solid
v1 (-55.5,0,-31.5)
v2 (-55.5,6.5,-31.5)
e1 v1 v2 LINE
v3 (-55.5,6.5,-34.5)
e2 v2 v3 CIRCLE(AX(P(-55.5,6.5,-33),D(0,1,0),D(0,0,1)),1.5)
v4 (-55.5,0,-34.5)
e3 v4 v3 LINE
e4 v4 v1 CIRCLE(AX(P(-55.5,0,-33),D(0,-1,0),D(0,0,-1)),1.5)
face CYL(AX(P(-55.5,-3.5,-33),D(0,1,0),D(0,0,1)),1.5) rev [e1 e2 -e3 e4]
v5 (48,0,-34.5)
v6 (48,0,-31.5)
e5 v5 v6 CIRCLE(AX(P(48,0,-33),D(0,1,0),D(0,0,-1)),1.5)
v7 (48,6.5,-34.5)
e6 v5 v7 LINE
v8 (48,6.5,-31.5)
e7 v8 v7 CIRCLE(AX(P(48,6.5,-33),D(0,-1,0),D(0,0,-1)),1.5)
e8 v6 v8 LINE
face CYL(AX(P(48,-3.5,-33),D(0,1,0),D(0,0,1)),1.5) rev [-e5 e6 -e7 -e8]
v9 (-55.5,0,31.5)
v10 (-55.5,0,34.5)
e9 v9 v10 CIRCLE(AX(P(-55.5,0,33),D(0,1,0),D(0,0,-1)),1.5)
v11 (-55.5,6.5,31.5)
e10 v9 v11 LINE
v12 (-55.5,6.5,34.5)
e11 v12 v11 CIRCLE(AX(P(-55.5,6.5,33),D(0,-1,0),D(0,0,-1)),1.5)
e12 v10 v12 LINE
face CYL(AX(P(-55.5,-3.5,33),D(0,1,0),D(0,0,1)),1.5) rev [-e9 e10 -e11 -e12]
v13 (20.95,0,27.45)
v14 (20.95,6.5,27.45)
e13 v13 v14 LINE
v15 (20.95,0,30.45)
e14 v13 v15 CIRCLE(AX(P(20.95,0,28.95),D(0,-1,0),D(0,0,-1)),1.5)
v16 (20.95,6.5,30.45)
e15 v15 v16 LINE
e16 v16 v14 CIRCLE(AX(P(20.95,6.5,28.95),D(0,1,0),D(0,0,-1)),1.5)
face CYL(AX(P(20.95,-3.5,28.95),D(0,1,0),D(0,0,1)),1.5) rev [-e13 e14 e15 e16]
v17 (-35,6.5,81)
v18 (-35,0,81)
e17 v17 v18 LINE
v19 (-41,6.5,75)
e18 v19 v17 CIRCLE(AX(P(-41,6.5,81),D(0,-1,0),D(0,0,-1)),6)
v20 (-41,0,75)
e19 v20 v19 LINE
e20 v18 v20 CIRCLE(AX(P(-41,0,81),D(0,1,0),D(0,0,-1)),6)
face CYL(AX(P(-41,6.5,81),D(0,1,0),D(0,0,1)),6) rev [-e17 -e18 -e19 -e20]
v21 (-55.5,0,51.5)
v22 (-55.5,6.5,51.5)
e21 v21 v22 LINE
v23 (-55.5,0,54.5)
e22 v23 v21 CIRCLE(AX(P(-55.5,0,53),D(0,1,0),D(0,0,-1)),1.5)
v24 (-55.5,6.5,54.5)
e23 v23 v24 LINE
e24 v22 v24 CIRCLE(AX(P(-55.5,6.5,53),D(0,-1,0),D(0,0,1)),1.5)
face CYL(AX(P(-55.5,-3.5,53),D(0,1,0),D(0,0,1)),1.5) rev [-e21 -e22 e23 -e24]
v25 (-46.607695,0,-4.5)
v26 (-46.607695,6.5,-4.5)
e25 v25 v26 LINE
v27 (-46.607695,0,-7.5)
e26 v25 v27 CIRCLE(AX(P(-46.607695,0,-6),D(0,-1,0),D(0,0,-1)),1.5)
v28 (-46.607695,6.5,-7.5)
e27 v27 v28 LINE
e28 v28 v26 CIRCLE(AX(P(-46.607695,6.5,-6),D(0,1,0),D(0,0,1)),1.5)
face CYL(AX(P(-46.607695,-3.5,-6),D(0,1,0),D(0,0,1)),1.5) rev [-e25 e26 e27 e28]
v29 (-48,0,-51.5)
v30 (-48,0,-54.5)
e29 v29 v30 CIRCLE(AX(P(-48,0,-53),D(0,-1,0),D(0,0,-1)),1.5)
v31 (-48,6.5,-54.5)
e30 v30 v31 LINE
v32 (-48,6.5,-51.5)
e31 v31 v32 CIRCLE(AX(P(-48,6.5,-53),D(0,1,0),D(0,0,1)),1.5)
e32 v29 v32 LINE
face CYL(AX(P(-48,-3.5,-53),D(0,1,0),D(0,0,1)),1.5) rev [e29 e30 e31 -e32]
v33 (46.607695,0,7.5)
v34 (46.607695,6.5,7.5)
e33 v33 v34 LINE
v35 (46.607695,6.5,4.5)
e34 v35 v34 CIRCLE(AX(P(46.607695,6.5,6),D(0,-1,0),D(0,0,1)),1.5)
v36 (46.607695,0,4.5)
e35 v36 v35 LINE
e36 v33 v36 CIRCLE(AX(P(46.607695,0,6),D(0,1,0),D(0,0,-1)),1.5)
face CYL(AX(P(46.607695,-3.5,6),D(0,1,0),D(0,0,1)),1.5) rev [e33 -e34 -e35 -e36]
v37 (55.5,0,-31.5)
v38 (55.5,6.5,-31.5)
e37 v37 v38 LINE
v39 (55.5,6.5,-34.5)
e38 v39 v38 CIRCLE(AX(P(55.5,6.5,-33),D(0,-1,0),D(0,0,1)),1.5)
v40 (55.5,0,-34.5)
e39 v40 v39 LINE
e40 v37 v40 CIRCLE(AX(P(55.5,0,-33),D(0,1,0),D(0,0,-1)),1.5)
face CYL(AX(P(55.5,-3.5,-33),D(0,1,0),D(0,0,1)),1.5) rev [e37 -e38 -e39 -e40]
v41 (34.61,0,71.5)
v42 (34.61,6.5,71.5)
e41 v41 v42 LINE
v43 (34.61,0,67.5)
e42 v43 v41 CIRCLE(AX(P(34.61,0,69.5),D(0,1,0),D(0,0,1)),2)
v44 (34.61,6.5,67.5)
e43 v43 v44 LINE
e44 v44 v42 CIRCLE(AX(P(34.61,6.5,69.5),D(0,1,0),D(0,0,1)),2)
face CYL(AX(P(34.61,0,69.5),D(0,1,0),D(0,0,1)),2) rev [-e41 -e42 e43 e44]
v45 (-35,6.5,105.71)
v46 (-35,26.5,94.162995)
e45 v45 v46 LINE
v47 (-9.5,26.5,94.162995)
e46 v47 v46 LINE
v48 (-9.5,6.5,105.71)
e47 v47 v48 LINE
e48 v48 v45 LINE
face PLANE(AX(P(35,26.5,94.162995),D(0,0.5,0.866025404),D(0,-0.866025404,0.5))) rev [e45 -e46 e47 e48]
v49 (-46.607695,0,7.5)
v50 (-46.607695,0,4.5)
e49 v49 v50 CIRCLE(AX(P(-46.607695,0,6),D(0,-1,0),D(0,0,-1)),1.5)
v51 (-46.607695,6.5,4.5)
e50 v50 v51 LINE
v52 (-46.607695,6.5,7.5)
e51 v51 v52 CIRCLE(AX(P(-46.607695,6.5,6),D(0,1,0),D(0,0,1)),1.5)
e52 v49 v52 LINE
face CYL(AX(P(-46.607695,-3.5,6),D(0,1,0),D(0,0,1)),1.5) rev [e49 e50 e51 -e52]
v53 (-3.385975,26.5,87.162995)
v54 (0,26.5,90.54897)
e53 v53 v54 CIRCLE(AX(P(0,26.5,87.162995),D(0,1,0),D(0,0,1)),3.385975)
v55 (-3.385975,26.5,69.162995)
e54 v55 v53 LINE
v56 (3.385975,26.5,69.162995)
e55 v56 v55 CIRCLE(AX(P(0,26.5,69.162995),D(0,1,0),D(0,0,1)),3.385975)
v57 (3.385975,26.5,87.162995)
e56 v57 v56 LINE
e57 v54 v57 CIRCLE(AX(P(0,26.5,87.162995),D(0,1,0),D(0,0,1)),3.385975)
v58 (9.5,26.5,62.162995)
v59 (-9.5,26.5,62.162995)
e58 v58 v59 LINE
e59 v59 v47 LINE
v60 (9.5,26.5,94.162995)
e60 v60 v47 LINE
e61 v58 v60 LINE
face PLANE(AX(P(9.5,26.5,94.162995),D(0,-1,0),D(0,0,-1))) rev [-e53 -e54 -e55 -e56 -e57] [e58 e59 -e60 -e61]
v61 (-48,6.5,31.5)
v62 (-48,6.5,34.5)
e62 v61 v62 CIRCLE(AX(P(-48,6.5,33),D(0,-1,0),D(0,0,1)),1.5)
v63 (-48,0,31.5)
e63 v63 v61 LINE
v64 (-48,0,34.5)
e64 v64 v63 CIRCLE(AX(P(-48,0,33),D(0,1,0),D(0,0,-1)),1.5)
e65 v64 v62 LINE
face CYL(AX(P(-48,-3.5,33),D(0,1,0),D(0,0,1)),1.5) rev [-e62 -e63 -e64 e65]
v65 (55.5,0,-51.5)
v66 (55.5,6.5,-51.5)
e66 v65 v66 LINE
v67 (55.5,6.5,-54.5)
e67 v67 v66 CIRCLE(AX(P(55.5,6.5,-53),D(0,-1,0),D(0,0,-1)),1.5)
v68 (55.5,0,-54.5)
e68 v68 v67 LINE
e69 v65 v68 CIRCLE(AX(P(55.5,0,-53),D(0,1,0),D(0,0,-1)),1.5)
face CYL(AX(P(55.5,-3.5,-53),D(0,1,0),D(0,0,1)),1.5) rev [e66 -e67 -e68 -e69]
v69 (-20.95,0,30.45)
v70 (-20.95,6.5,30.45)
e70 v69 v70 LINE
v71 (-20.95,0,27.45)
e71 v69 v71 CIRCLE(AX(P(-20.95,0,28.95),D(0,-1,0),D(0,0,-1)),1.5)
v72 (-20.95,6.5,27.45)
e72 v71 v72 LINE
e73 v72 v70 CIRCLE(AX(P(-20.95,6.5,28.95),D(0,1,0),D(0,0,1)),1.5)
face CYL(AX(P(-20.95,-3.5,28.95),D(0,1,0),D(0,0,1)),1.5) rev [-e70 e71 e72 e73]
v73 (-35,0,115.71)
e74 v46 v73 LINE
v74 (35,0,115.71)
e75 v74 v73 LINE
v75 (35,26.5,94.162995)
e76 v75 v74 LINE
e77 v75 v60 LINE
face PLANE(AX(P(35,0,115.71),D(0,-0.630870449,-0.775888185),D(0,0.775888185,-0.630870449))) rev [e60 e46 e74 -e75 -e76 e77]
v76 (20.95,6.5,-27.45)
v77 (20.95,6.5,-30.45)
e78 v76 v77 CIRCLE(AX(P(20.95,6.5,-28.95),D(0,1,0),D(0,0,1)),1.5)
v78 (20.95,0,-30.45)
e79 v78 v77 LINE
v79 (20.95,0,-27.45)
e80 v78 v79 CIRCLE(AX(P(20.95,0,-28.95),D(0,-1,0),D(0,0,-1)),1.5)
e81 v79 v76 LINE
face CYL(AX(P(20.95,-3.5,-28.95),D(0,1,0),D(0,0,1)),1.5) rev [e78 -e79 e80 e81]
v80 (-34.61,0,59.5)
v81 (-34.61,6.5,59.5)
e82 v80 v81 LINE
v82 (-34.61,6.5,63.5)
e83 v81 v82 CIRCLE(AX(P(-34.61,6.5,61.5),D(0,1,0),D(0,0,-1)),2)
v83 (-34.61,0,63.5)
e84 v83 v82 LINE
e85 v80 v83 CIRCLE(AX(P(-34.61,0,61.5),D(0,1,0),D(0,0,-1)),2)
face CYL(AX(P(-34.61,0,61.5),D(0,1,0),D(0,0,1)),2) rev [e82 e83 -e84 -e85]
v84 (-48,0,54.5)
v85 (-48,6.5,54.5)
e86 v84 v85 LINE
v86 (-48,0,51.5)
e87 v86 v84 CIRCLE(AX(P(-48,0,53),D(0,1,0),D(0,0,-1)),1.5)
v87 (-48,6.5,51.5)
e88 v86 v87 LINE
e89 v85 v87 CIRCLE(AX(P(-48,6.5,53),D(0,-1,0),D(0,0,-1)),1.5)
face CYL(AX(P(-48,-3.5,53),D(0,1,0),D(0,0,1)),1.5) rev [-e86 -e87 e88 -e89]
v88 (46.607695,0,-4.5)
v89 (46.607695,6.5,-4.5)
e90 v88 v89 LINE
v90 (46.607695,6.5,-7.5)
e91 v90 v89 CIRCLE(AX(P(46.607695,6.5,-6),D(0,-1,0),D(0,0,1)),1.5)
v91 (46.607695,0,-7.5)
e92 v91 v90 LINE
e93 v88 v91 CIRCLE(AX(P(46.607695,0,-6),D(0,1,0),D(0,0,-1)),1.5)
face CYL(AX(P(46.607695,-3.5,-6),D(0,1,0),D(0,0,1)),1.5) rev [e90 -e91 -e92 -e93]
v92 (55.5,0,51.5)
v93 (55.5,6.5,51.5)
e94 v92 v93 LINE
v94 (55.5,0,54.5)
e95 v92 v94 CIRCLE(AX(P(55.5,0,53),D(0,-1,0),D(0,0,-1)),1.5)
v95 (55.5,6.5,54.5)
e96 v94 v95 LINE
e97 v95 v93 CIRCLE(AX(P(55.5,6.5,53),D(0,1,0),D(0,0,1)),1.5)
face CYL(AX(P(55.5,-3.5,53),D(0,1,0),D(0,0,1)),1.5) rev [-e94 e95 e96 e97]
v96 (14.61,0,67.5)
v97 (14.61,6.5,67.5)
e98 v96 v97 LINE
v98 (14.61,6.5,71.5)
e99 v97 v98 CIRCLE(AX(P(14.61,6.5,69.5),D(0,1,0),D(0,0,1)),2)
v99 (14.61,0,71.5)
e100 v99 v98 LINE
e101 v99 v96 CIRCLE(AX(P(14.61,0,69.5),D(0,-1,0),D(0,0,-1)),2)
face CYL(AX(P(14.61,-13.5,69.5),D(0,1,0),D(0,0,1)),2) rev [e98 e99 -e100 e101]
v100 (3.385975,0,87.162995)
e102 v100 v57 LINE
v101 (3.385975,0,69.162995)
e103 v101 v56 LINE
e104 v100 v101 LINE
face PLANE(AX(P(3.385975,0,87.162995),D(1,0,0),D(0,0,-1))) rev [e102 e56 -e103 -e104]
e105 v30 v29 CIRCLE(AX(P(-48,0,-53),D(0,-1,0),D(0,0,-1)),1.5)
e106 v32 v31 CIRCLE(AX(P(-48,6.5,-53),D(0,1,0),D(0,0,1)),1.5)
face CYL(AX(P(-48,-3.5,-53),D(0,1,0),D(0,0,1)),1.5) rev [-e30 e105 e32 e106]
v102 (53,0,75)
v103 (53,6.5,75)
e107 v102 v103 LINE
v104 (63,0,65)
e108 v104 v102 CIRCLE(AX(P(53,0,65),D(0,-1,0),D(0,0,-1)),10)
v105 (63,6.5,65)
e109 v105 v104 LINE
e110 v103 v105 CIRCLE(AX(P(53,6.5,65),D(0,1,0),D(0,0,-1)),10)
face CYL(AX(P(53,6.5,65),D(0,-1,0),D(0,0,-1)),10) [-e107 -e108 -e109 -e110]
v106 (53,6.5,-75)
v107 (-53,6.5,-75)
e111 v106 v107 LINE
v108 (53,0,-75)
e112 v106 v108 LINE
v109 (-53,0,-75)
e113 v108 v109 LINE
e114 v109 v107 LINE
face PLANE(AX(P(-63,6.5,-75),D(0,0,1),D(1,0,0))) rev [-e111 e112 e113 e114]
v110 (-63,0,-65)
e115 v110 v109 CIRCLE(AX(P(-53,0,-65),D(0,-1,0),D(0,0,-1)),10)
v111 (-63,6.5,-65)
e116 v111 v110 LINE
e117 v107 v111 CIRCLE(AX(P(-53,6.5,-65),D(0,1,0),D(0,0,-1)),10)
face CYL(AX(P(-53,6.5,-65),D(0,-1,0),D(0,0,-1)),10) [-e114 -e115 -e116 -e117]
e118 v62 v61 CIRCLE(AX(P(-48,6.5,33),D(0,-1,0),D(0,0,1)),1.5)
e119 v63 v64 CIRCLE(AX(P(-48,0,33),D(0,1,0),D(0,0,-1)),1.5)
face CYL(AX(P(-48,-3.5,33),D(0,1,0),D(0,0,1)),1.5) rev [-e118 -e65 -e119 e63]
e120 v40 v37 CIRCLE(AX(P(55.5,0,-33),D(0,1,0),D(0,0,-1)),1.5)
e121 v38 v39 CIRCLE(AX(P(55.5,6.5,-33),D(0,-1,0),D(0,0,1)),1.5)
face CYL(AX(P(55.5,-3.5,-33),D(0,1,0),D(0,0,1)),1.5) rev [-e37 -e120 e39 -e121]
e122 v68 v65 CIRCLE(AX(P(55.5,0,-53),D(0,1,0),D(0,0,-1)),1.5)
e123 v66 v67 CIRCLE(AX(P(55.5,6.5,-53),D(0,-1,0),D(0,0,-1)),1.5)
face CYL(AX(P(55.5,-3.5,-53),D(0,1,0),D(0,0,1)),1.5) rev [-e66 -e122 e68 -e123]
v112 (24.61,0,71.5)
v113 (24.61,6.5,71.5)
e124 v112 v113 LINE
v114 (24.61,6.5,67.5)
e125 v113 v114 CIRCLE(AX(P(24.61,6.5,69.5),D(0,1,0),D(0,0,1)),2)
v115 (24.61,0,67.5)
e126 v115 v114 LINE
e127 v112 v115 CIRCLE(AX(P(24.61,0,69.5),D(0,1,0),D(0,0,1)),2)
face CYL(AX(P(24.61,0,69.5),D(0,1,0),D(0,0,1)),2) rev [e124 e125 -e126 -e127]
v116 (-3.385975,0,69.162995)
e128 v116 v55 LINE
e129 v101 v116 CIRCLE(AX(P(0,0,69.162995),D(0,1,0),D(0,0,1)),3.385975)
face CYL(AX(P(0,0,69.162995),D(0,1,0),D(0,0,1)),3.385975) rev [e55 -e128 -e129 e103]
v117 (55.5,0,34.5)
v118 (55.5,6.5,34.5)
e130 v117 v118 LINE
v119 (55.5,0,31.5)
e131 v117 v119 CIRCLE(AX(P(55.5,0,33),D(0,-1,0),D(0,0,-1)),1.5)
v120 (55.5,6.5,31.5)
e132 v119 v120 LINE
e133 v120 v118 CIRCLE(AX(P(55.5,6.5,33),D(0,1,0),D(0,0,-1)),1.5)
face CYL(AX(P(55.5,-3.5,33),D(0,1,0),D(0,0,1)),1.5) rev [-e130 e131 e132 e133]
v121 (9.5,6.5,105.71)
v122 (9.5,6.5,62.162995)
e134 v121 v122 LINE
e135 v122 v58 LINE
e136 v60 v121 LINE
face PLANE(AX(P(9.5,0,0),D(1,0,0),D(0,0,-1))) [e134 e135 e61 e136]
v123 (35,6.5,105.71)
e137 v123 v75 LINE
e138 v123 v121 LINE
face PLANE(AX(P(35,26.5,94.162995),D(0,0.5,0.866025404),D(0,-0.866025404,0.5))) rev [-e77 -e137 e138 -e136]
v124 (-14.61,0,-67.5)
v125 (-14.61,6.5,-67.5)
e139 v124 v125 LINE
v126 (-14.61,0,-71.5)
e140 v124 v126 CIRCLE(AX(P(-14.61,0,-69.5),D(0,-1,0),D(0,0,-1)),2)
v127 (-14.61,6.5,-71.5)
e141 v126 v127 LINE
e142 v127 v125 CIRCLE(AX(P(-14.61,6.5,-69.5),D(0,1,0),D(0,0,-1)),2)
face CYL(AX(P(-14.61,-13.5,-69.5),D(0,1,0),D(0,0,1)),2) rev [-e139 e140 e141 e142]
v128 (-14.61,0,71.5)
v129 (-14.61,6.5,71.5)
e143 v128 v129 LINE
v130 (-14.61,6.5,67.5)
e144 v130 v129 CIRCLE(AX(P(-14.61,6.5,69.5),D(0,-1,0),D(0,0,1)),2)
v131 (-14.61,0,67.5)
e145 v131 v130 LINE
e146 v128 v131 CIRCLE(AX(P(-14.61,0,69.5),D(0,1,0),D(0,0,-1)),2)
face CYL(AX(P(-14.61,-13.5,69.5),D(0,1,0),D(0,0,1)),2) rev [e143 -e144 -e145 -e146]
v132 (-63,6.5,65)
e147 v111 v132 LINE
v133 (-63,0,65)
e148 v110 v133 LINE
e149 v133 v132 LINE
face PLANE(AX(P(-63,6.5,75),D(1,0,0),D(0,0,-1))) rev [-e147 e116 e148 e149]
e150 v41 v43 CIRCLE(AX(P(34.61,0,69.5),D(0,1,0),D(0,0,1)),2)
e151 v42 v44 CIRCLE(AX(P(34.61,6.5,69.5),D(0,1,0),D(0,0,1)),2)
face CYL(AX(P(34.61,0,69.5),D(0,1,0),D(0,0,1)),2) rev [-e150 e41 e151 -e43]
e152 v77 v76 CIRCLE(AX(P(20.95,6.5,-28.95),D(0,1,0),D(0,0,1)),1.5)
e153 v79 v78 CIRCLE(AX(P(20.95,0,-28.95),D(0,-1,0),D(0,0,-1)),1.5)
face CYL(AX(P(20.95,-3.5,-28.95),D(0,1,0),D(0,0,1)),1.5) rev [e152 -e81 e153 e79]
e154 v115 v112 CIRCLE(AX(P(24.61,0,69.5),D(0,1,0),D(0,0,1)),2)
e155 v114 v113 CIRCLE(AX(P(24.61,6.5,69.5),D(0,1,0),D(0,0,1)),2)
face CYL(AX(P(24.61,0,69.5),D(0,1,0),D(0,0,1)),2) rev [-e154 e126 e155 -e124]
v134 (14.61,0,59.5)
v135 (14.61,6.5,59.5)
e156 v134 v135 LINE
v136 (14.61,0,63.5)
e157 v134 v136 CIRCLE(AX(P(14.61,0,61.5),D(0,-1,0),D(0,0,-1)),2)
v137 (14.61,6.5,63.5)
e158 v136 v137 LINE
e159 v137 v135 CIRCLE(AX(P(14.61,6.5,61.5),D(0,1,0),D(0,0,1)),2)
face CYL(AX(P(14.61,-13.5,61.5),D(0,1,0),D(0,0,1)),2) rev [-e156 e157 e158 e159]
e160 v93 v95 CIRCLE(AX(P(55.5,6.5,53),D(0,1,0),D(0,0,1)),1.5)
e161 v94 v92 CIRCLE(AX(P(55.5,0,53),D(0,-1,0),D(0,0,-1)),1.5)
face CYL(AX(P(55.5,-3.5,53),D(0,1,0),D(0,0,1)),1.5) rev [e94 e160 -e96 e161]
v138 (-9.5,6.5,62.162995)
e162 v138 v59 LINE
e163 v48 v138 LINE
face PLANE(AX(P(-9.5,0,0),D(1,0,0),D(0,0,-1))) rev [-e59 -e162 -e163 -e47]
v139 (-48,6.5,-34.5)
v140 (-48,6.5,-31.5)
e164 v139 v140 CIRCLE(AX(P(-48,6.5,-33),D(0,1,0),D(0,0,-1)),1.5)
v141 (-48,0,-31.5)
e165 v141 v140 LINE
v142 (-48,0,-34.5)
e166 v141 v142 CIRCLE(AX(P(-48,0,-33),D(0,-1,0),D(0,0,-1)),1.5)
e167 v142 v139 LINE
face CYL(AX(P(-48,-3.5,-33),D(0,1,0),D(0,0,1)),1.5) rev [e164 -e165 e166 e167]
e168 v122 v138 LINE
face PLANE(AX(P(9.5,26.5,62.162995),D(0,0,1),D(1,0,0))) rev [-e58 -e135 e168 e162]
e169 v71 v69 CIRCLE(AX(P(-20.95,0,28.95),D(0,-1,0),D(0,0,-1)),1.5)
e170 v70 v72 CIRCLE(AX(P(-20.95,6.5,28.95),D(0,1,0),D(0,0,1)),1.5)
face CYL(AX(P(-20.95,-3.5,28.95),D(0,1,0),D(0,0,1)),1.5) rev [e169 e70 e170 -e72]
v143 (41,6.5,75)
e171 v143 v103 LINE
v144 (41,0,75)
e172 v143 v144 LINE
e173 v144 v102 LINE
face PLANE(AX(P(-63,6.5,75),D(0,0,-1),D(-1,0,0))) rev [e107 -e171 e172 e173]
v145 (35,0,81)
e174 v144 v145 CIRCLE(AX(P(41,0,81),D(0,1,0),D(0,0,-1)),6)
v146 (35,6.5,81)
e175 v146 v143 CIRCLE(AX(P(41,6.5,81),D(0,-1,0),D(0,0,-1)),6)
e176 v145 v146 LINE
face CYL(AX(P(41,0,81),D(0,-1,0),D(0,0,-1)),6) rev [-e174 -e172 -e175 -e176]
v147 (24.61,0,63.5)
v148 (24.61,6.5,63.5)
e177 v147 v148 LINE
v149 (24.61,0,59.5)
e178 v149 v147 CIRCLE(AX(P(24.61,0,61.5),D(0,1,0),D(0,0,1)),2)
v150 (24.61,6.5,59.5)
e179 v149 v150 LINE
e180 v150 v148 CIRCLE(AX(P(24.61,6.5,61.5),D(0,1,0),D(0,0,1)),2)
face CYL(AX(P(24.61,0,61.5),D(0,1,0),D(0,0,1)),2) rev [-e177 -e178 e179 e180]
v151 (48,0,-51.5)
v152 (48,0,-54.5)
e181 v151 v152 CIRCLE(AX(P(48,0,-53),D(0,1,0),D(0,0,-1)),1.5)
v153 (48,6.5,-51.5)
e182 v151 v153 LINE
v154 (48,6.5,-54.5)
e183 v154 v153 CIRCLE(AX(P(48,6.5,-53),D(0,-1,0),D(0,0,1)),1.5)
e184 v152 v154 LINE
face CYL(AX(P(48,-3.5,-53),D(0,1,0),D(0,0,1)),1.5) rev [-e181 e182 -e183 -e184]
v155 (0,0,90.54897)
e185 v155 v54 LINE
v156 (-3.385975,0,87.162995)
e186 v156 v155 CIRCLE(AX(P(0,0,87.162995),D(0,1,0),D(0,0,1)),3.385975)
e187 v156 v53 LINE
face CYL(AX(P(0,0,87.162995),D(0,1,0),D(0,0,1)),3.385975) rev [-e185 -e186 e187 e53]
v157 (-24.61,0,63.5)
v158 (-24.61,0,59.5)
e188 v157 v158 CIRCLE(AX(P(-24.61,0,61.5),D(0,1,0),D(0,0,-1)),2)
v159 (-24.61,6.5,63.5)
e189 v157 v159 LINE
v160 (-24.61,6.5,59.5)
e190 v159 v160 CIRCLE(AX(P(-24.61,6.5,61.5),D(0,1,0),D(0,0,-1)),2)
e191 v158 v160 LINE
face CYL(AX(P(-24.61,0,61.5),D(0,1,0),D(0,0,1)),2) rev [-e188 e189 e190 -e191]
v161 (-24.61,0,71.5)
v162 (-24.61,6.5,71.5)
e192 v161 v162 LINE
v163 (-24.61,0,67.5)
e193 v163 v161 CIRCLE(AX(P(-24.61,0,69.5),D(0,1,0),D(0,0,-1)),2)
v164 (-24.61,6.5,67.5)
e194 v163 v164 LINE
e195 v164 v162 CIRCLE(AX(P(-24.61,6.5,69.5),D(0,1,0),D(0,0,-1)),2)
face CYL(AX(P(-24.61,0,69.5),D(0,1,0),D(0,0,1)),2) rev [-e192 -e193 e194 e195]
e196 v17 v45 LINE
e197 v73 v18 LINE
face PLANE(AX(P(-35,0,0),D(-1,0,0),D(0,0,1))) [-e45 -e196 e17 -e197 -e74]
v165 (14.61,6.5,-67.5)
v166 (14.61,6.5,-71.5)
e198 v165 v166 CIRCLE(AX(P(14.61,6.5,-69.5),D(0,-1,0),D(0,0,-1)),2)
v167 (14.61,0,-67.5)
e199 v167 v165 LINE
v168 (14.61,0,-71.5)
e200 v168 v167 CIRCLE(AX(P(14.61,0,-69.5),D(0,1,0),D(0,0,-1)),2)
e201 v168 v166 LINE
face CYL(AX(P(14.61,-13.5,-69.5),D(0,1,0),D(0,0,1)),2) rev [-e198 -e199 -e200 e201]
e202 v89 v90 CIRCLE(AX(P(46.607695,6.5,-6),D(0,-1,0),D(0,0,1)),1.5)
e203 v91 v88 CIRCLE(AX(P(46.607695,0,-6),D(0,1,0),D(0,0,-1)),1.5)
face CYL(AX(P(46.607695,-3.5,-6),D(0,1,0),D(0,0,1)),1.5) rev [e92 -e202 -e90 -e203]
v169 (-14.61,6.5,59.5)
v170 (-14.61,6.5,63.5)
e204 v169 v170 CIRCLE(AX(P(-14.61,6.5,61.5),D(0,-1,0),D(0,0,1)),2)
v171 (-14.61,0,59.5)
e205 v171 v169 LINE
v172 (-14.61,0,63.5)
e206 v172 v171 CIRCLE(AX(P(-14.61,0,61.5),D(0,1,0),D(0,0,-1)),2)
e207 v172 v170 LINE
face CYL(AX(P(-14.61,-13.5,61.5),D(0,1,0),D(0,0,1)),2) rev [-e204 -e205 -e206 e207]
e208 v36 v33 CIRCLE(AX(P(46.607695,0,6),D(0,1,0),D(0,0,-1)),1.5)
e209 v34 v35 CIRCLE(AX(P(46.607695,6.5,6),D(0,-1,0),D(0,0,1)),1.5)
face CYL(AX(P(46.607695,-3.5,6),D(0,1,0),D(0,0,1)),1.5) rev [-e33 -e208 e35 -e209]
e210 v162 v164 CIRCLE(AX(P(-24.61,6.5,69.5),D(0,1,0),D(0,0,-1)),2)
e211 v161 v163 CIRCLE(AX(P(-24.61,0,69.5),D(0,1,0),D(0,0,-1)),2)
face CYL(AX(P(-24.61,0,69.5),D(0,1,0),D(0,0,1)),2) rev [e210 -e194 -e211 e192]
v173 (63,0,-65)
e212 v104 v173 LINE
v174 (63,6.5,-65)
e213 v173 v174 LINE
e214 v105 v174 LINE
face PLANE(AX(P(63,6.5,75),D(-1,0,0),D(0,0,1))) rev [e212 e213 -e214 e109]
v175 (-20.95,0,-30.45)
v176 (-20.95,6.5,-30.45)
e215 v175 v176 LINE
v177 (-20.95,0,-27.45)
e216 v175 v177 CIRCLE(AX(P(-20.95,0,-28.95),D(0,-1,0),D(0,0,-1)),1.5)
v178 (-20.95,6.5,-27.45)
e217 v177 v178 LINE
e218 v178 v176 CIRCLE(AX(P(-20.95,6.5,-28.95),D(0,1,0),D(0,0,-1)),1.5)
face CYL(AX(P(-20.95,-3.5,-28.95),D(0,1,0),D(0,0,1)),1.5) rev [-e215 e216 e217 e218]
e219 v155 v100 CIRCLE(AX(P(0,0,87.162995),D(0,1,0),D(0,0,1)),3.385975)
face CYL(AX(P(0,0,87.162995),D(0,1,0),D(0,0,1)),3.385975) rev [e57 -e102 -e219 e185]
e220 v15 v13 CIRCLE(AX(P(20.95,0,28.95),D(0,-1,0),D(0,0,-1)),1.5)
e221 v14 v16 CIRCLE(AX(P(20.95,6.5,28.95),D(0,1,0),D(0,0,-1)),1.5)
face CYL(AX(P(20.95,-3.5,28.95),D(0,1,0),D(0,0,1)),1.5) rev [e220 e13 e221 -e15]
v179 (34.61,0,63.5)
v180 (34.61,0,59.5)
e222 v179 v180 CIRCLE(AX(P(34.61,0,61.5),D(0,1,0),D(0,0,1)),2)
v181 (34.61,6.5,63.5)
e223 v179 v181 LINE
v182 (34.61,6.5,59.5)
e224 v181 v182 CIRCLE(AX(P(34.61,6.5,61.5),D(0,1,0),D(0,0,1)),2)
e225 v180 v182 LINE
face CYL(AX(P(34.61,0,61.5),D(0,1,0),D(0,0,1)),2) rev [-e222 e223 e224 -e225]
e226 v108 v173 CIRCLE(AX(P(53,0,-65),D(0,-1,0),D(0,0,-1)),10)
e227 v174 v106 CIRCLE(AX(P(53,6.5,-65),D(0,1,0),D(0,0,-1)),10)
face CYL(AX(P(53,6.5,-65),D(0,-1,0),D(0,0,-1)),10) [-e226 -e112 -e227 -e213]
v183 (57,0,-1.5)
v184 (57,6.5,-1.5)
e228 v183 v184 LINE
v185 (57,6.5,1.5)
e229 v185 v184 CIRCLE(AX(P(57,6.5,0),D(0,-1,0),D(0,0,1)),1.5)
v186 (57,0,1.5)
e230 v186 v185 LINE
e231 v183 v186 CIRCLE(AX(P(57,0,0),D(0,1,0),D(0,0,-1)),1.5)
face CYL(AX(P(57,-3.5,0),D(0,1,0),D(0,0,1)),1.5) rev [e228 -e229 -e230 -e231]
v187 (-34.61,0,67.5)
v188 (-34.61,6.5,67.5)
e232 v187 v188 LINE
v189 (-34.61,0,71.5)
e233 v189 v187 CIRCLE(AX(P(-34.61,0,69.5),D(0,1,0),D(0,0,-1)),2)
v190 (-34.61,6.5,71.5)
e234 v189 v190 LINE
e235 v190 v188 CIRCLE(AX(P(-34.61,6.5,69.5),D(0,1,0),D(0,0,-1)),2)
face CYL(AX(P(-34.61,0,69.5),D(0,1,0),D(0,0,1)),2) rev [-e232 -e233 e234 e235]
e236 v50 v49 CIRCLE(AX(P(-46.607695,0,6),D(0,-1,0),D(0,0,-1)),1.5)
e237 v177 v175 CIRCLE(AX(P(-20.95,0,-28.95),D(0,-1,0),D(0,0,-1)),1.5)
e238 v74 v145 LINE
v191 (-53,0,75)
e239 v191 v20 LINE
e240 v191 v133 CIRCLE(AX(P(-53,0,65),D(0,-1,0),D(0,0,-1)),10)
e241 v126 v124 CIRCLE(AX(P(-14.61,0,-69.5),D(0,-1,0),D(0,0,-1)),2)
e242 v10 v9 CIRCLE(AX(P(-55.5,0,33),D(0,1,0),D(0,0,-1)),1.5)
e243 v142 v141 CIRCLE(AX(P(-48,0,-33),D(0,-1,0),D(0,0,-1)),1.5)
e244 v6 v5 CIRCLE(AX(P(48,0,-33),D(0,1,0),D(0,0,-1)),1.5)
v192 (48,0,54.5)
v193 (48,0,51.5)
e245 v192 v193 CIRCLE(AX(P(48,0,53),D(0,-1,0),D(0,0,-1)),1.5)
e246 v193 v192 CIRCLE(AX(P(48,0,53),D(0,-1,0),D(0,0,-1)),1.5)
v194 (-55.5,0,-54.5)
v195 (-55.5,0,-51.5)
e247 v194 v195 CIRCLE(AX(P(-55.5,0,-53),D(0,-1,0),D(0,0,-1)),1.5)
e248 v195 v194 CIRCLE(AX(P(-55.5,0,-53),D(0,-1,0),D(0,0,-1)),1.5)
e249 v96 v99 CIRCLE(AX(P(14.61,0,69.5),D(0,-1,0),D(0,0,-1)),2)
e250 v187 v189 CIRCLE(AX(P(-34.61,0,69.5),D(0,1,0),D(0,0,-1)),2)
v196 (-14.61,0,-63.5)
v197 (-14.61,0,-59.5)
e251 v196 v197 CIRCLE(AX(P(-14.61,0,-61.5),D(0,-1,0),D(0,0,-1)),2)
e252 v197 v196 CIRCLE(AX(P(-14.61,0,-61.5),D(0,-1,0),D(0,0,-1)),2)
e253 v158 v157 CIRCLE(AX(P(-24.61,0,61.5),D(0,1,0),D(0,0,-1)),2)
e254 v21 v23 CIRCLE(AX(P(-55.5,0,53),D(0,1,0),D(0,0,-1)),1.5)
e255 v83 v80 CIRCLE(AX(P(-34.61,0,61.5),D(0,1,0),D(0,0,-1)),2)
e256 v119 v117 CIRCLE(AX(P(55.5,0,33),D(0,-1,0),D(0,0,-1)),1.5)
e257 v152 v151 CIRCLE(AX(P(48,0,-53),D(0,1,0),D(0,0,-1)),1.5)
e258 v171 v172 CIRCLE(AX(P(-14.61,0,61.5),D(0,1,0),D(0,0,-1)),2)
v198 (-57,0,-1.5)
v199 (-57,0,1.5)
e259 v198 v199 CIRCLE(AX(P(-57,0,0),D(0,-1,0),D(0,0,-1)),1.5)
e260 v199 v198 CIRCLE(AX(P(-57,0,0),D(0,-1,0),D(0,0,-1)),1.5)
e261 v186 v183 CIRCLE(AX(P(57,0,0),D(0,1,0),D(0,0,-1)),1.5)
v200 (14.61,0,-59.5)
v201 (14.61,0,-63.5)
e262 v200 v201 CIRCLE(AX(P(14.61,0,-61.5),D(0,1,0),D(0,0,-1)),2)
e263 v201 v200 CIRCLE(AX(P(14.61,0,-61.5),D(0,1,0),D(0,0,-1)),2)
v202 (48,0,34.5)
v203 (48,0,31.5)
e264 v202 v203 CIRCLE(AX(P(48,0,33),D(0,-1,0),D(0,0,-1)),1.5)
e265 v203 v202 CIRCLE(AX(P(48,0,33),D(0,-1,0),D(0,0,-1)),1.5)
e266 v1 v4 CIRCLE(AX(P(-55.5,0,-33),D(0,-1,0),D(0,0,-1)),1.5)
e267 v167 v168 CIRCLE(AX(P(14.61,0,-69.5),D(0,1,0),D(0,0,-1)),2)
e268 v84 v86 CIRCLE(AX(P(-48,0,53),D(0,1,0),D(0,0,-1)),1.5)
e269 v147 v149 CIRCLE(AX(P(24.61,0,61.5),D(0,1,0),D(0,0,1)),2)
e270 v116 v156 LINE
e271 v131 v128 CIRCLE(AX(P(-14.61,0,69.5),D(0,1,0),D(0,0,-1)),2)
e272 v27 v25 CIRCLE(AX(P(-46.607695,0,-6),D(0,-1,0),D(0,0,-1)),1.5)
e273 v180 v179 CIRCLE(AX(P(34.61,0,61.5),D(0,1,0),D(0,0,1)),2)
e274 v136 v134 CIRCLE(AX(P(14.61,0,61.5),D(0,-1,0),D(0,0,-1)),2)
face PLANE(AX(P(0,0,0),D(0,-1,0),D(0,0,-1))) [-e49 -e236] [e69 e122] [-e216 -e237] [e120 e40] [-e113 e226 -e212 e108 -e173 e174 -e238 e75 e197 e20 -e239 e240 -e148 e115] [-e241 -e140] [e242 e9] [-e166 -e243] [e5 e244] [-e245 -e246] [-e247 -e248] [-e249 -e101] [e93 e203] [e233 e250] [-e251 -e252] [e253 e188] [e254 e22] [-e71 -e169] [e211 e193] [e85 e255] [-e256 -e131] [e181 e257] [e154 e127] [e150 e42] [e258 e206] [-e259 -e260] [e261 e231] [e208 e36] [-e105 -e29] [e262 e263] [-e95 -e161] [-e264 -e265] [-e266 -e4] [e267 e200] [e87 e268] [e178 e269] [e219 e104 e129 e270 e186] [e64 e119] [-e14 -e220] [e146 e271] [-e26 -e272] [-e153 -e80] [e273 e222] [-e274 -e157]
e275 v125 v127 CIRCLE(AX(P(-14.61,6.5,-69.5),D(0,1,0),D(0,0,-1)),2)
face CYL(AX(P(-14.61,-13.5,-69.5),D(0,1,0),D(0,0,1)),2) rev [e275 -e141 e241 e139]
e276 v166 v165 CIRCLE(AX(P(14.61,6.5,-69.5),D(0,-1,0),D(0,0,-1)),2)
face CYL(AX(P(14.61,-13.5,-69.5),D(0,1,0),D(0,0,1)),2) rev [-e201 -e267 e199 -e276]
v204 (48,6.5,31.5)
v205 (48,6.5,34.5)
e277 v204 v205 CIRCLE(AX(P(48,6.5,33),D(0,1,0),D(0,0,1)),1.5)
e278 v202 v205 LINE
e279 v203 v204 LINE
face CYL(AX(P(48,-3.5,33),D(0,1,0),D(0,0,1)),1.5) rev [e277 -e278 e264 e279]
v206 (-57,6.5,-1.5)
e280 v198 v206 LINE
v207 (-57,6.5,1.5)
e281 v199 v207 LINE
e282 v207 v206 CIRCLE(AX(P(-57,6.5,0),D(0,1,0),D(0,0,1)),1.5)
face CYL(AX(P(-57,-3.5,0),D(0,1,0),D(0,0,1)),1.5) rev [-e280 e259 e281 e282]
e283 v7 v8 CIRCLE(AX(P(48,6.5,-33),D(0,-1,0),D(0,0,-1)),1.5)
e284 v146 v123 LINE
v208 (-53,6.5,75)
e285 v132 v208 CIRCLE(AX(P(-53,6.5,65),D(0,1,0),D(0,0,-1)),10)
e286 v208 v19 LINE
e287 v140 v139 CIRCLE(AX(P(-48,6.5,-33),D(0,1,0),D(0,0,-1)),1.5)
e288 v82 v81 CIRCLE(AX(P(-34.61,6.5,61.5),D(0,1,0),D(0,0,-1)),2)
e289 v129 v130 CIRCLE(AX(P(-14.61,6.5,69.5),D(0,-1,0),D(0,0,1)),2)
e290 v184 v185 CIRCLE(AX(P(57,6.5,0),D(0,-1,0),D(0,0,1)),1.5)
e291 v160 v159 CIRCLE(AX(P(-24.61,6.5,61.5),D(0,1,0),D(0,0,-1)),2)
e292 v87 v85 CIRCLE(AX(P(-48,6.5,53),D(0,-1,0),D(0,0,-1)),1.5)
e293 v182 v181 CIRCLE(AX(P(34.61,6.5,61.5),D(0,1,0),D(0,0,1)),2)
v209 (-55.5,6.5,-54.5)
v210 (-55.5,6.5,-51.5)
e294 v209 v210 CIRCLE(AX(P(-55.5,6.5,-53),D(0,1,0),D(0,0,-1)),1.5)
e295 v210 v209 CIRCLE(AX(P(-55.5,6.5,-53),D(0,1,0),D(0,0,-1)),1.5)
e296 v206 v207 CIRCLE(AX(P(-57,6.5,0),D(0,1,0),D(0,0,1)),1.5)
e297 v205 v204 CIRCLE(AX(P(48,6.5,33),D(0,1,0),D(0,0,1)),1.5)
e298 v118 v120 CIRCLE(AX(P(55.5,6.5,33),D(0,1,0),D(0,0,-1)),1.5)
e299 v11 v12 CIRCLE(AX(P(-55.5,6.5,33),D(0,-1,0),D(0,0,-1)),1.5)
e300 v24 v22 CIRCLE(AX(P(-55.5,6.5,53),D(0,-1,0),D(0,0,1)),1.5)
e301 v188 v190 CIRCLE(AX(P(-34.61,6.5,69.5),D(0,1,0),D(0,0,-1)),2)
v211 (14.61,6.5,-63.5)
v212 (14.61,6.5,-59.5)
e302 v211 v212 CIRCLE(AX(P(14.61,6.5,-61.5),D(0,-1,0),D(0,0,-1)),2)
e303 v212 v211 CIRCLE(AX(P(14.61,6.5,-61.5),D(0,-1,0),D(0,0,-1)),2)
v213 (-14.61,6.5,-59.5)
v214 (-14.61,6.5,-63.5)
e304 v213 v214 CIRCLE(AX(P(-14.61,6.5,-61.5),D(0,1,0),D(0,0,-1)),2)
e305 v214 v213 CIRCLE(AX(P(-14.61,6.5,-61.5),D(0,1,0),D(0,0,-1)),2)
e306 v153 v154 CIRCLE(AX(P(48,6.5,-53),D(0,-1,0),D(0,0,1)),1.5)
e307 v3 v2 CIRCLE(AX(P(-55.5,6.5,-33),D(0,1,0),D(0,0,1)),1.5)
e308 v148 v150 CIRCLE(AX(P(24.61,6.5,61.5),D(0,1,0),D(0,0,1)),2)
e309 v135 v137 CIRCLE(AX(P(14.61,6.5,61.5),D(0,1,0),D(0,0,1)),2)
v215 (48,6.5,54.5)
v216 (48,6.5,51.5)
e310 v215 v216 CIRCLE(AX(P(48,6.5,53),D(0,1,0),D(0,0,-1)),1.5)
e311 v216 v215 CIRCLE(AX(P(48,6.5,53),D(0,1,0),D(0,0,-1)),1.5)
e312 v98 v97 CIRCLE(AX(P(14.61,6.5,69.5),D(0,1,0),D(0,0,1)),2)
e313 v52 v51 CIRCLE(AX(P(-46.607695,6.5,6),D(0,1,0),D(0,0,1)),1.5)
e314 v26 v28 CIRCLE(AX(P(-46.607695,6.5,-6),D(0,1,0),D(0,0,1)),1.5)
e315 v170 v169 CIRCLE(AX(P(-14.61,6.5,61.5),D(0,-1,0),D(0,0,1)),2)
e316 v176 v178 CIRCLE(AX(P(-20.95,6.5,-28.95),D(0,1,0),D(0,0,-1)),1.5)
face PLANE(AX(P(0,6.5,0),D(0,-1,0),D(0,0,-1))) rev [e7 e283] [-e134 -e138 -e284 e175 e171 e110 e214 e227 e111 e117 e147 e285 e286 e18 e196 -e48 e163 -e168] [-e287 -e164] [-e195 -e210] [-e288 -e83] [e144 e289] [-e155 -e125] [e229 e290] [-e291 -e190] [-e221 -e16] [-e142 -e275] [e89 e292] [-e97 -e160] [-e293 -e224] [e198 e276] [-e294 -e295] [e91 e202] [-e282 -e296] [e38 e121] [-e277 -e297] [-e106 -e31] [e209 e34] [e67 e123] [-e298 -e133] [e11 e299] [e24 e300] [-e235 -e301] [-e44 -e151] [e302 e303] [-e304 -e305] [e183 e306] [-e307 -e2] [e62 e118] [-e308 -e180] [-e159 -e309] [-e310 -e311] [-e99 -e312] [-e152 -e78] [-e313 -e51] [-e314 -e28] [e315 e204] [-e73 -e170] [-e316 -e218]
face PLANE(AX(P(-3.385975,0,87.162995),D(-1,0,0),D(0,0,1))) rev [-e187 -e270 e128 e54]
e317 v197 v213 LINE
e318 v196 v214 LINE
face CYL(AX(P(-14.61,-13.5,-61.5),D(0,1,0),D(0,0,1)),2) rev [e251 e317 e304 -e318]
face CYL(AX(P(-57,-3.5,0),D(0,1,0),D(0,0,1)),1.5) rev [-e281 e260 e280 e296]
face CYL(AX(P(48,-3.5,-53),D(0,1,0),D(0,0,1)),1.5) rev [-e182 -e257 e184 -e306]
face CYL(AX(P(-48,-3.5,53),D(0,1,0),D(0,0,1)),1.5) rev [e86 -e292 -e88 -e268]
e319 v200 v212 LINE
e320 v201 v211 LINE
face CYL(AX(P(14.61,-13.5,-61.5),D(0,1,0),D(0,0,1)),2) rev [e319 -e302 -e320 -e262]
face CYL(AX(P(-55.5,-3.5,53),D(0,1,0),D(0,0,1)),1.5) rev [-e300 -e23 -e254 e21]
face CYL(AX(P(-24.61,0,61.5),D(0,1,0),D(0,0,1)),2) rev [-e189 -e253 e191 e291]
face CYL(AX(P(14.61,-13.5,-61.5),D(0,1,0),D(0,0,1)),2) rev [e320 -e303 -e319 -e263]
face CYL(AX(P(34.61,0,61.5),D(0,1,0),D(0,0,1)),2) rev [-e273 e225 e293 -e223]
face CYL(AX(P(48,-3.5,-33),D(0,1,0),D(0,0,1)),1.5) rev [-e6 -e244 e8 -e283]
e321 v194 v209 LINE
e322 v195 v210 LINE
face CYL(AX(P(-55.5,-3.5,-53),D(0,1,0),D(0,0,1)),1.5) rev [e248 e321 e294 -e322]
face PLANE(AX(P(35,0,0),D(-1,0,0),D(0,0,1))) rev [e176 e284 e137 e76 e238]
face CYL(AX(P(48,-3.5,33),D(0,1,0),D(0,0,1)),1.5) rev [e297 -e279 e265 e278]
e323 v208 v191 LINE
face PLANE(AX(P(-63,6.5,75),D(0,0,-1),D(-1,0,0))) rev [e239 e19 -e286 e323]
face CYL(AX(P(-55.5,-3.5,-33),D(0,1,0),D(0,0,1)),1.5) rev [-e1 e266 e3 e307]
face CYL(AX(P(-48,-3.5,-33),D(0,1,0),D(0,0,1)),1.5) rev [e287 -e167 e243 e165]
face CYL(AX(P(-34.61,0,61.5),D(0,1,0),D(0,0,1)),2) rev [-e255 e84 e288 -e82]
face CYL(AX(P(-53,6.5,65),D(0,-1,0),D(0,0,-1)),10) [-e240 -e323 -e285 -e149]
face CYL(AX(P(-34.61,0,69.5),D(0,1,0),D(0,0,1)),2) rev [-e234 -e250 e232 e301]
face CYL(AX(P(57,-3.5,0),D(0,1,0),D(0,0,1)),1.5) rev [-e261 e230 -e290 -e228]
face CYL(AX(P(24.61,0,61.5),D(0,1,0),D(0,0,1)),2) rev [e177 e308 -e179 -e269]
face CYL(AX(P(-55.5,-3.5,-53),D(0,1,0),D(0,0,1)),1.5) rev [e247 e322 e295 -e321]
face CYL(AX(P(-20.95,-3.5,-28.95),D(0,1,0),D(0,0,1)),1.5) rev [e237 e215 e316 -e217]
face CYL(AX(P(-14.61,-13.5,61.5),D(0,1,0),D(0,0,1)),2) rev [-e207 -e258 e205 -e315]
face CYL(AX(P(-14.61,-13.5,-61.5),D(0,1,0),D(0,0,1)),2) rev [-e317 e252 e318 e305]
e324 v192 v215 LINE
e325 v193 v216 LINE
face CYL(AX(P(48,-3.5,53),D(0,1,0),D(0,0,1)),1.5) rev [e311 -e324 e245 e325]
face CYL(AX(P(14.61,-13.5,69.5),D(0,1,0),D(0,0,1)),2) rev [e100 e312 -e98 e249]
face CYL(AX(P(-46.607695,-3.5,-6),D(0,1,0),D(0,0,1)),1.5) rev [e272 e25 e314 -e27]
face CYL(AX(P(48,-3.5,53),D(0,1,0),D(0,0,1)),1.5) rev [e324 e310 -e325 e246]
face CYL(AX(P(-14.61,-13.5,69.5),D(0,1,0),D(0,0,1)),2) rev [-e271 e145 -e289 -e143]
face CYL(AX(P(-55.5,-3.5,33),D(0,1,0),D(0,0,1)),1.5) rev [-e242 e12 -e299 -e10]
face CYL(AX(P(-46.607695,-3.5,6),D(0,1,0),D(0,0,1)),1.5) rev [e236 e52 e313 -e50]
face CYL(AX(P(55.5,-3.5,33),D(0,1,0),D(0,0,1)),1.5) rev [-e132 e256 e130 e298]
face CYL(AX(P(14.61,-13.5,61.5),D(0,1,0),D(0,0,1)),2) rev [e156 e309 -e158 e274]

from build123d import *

# Parameters (mm, degrees)
SKETCH1_W               = 126
SKETCH1_H               = 150
BOSS_EXTRUDE1_DEPTH     = 6.5
SKETCH2_R               = 1.5
CUT_EXTRUDE1_DEPTH      = 10
MIRROR2_COPY_1_SKETCH_R = 1.5
MIRROR2_COPY_1_DEPTH    = 10
SKETCH3_R               = 1.5
CUT_EXTRUDE2_DEPTH      = 10
FILLET1_R               = 10
SKETCH4_R               = 1.5
CUT_EXTRUDE3_DEPTH      = 10
SKETCH5_R               = 2
CUT_EXTRUDE4_DEPTH      = 20
MIRROR5_COPY_1_SKETCH_R = 2
MIRROR5_COPY_1_DEPTH    = 20
SKETCH6_R               = 2
CUT_EXTRUDE5_DEPTH      = 99.164402917
BOSS_EXTRUDE3_DEPTH     = 35
BOSS_EXTRUDE4_DEPTH     = 9.5
CUT_EXTRUDE6_DEPTH      = 135.387700702
FILLET2_R               = 6


with BuildPart() as part:
    # Sketch1 → Boss-Extrude1 (new body)
    with BuildSketch(Plane(origin=(0, 0, 0), x_dir=(1, 0, 0), z_dir=(0, 1, 0))):
        Rectangle(SKETCH1_W, SKETCH1_H)
    extrude(amount=BOSS_EXTRUDE1_DEPTH)

    # Sketch2 → Cut-Extrude1 (cut)
    with BuildSketch(Plane(origin=(0, 6.5, 0), x_dir=(1, 0, 0), z_dir=(0, 1, 0))):
        with Locations(Location((-55.5, 33, 0), (0, 0, 270))):
            Circle(SKETCH2_R)
        with Locations(Location((-48, 33, 0), (0, 0, 90))):
            Circle(SKETCH2_R)
        with Locations(Location((-48, 53, 0), (0, 0, 270))):
            Circle(SKETCH2_R)
        with Locations(Location((-55.5, 53, 0), (0, 0, 90))):
            Circle(SKETCH2_R)
    cut_extrude1 = extrude(amount=-CUT_EXTRUDE1_DEPTH, mode=Mode.SUBTRACT)

    # Mirror1: Cut-Extrude1 across plane
    add(cut_extrude1.mirror(Plane(origin=(0, 0, 0), x_dir=(0, 0, 1), z_dir=(1, 0, 0))), mode=Mode.SUBTRACT)

    # Mirror2: Cut-Extrude1 across plane
    add(cut_extrude1.mirror(Plane.XY), mode=Mode.SUBTRACT)

    # Mirror2 copy 1 sketch → Mirror2 copy 1 (cut)
    with BuildSketch(Plane(origin=(0, 6.5, 0), x_dir=(-1, 0, 0), z_dir=(0, 1, 0))):
        with Locations(Location((-55.5, 33, 0), (0, 0, 270))):
            Circle(MIRROR2_COPY_1_SKETCH_R)
        with Locations(Location((-48, 33, 0), (0, 0, 90))):
            Circle(MIRROR2_COPY_1_SKETCH_R)
        with Locations(Location((-48, 53, 0), (0, 0, 270))):
            Circle(MIRROR2_COPY_1_SKETCH_R)
        with Locations(Location((-55.5, 53, 0), (0, 0, 90))):
            Circle(MIRROR2_COPY_1_SKETCH_R)
    extrude(amount=-MIRROR2_COPY_1_DEPTH, mode=Mode.SUBTRACT)

    # Sketch3 → Cut-Extrude2 (cut)
    with BuildSketch(Plane(origin=(0, 6.5, 0), x_dir=(1, 0, 0), z_dir=(0, 1, 0))):
        with Locations(Location((-20.95, -28.95, 0), (0, 0, 270))):
            Circle(SKETCH3_R)
        with Locations(Location((20.95, -28.95, 0), (0, 0, 90))):
            Circle(SKETCH3_R)
        with Locations(Location((20.95, 28.95, 0), (0, 0, 270))):
            Circle(SKETCH3_R)
        with Locations(Location((-20.95, 28.95, 0), (0, 0, 90))):
            Circle(SKETCH3_R)
    extrude(amount=-CUT_EXTRUDE2_DEPTH, mode=Mode.SUBTRACT)

    # Fillet1
    fillet1_edges = [part.edges().sort_by_distance(p)[0] for p in [
        (63, 3.25, 75),
        (-63, 3.25, 75),
        (-63, 3.25, -75),
        (63, 3.25, -75),
    ]]
    fillet(fillet1_edges, radius=FILLET1_R)

    # Sketch4 → Cut-Extrude3 (cut)
    with BuildSketch(Plane(origin=(0, 6.5, 0), x_dir=(1, 0, 0), z_dir=(0, 1, 0))):
        with Locations(Location((-46.607695155, -6, 0), (0, 0, 270))):
            Circle(SKETCH4_R)
        with Locations(Location((-46.607695155, 6, 0), (0, 0, 270))):
            Circle(SKETCH4_R)
        with Locations(Location((-57, 0, 0), (0, 0, 270))):
            Circle(SKETCH4_R)
    cut_extrude3 = extrude(amount=-CUT_EXTRUDE3_DEPTH, mode=Mode.SUBTRACT)

    # Mirror3: Cut-Extrude3 across plane
    add(cut_extrude3.mirror(Plane(origin=(0, 0, 0), x_dir=(0, 0, 1), z_dir=(1, 0, 0))), mode=Mode.SUBTRACT)

    # Sketch5 → Cut-Extrude4 (cut)
    with BuildSketch(Plane(origin=(0, 6.5, 0), x_dir=(1, 0, 0), z_dir=(0, 1, 0))):
        with Locations(Location((14.61, -61.5, 0), (0, 0, 270))):
            Circle(SKETCH5_R)
        with Locations(Location((14.61, -69.5, 0), (0, 0, 270))):
            Circle(SKETCH5_R)
    cut_extrude4 = extrude(amount=-CUT_EXTRUDE4_DEPTH, mode=Mode.SUBTRACT)

    # Mirror4: Cut-Extrude4 across plane
    add(cut_extrude4.mirror(Plane(origin=(0, 0, 0), x_dir=(0, 0, 1), z_dir=(1, 0, 0))), mode=Mode.SUBTRACT)

    # Mirror5: Cut-Extrude4 across plane
    add(cut_extrude4.mirror(Plane.XY), mode=Mode.SUBTRACT)

    # Mirror5 copy 1 sketch → Mirror5 copy 1 (cut)
    with BuildSketch(Plane(origin=(0, 6.5, 0), x_dir=(-1, 0, 0), z_dir=(0, 1, 0))):
        with Locations(Location((14.61, -61.5, 0), (0, 0, 270))):
            Circle(MIRROR5_COPY_1_SKETCH_R)
        with Locations(Location((14.61, -69.5, 0), (0, 0, 270))):
            Circle(MIRROR5_COPY_1_SKETCH_R)
    extrude(amount=-MIRROR5_COPY_1_DEPTH, mode=Mode.SUBTRACT)

    # Sketch6 → Cut-Extrude5 (cut, through all)
    with BuildSketch(Plane(origin=(0, 6.5, 0), x_dir=(1, 0, 0), z_dir=(0, 1, 0))):
        with Locations(Location((14.61, -69.5, 0), (0, 0, 270))):
            Circle(SKETCH6_R)
        with Locations(Location((14.61, -61.5, 0), (0, 0, 270))):
            Circle(SKETCH6_R)
        with Locations(Location((24.61, -69.5, 0), (0, 0, 270))):
            Circle(SKETCH6_R)
        with Locations(Location((24.61, -61.5, 0), (0, 0, 270))):
            Circle(SKETCH6_R)
        with Locations(Location((34.61, -69.5, 0), (0, 0, 270))):
            Circle(SKETCH6_R)
        with Locations(Location((34.61, -61.5, 0), (0, 0, 270))):
            Circle(SKETCH6_R)
        with Locations(Location((-34.61, -61.5, 0), (0, 0, 270))):
            Circle(SKETCH6_R)
        with Locations(Location((-34.61, -69.5, 0), (0, 0, 270))):
            Circle(SKETCH6_R)
        with Locations(Location((-24.61, -61.5, 0), (0, 0, 270))):
            Circle(SKETCH6_R)
        with Locations(Location((-24.61, -69.5, 0), (0, 0, 270))):
            Circle(SKETCH6_R)
        with Locations(Location((-14.61, -61.5, 0), (0, 0, 270))):
            Circle(SKETCH6_R)
        with Locations(Location((-14.61, -69.5, 0), (0, 0, 270))):
            Circle(SKETCH6_R)
    extrude(amount=-CUT_EXTRUDE5_DEPTH, mode=Mode.SUBTRACT)

    # Sketch8 → Boss-Extrude3 (add, symmetric)
    with BuildSketch(Plane(origin=(0, 0, 0), x_dir=(0, 0, -1), z_dir=(1, 0, 0))):
        Polygon((-75, 0), (-115.71, 0), (-94.162994616, 26.5), (-105.71, 6.5), (-75, 6.5), align=None)
    extrude(amount=BOSS_EXTRUDE3_DEPTH, both=True)

    # Sketch9 → Boss-Extrude4 (add, symmetric)
    with BuildSketch(Plane(origin=(0, 0, 0), x_dir=(0, 0, -1), z_dir=(1, 0, 0))):
        Polygon((-94.162994616, 26.5), (-62.162994616, 26.5), (-62.162994616, 6.5), (-75, 6.5), (-105.71, 6.5), align=None)
    extrude(amount=BOSS_EXTRUDE4_DEPTH, both=True)

    # Sketch10 → Cut-Extrude6 (cut, through all)
    with BuildSketch(Plane(origin=(0, 26.5, 0), x_dir=(1, 0, 0), z_dir=(0, 1, 0))):
        with BuildLine():
            Line((-3.385975304, -87.162994616), (-3.385975304, -69.162994616))
            ThreePointArc((-3.385975304, -69.162994616), (0, -65.777019313), (3.385975304, -69.162994616))
            Line((3.385975304, -69.162994616), (3.385975304, -87.162994616))
            ThreePointArc((3.385975304, -87.162994616), (0, -90.54896992), (-3.385975304, -87.162994616))
        make_face()
    extrude(amount=-CUT_EXTRUDE6_DEPTH, mode=Mode.SUBTRACT)

    # Fillet2
    fillet2_edges = [part.edges().sort_by_distance(p)[0] for p in [
        (-35, 3.25, 75),
        (35, 3.25, 75),
    ]]
    fillet(fillet2_edges, radius=FILLET2_R)


solid = part.part
